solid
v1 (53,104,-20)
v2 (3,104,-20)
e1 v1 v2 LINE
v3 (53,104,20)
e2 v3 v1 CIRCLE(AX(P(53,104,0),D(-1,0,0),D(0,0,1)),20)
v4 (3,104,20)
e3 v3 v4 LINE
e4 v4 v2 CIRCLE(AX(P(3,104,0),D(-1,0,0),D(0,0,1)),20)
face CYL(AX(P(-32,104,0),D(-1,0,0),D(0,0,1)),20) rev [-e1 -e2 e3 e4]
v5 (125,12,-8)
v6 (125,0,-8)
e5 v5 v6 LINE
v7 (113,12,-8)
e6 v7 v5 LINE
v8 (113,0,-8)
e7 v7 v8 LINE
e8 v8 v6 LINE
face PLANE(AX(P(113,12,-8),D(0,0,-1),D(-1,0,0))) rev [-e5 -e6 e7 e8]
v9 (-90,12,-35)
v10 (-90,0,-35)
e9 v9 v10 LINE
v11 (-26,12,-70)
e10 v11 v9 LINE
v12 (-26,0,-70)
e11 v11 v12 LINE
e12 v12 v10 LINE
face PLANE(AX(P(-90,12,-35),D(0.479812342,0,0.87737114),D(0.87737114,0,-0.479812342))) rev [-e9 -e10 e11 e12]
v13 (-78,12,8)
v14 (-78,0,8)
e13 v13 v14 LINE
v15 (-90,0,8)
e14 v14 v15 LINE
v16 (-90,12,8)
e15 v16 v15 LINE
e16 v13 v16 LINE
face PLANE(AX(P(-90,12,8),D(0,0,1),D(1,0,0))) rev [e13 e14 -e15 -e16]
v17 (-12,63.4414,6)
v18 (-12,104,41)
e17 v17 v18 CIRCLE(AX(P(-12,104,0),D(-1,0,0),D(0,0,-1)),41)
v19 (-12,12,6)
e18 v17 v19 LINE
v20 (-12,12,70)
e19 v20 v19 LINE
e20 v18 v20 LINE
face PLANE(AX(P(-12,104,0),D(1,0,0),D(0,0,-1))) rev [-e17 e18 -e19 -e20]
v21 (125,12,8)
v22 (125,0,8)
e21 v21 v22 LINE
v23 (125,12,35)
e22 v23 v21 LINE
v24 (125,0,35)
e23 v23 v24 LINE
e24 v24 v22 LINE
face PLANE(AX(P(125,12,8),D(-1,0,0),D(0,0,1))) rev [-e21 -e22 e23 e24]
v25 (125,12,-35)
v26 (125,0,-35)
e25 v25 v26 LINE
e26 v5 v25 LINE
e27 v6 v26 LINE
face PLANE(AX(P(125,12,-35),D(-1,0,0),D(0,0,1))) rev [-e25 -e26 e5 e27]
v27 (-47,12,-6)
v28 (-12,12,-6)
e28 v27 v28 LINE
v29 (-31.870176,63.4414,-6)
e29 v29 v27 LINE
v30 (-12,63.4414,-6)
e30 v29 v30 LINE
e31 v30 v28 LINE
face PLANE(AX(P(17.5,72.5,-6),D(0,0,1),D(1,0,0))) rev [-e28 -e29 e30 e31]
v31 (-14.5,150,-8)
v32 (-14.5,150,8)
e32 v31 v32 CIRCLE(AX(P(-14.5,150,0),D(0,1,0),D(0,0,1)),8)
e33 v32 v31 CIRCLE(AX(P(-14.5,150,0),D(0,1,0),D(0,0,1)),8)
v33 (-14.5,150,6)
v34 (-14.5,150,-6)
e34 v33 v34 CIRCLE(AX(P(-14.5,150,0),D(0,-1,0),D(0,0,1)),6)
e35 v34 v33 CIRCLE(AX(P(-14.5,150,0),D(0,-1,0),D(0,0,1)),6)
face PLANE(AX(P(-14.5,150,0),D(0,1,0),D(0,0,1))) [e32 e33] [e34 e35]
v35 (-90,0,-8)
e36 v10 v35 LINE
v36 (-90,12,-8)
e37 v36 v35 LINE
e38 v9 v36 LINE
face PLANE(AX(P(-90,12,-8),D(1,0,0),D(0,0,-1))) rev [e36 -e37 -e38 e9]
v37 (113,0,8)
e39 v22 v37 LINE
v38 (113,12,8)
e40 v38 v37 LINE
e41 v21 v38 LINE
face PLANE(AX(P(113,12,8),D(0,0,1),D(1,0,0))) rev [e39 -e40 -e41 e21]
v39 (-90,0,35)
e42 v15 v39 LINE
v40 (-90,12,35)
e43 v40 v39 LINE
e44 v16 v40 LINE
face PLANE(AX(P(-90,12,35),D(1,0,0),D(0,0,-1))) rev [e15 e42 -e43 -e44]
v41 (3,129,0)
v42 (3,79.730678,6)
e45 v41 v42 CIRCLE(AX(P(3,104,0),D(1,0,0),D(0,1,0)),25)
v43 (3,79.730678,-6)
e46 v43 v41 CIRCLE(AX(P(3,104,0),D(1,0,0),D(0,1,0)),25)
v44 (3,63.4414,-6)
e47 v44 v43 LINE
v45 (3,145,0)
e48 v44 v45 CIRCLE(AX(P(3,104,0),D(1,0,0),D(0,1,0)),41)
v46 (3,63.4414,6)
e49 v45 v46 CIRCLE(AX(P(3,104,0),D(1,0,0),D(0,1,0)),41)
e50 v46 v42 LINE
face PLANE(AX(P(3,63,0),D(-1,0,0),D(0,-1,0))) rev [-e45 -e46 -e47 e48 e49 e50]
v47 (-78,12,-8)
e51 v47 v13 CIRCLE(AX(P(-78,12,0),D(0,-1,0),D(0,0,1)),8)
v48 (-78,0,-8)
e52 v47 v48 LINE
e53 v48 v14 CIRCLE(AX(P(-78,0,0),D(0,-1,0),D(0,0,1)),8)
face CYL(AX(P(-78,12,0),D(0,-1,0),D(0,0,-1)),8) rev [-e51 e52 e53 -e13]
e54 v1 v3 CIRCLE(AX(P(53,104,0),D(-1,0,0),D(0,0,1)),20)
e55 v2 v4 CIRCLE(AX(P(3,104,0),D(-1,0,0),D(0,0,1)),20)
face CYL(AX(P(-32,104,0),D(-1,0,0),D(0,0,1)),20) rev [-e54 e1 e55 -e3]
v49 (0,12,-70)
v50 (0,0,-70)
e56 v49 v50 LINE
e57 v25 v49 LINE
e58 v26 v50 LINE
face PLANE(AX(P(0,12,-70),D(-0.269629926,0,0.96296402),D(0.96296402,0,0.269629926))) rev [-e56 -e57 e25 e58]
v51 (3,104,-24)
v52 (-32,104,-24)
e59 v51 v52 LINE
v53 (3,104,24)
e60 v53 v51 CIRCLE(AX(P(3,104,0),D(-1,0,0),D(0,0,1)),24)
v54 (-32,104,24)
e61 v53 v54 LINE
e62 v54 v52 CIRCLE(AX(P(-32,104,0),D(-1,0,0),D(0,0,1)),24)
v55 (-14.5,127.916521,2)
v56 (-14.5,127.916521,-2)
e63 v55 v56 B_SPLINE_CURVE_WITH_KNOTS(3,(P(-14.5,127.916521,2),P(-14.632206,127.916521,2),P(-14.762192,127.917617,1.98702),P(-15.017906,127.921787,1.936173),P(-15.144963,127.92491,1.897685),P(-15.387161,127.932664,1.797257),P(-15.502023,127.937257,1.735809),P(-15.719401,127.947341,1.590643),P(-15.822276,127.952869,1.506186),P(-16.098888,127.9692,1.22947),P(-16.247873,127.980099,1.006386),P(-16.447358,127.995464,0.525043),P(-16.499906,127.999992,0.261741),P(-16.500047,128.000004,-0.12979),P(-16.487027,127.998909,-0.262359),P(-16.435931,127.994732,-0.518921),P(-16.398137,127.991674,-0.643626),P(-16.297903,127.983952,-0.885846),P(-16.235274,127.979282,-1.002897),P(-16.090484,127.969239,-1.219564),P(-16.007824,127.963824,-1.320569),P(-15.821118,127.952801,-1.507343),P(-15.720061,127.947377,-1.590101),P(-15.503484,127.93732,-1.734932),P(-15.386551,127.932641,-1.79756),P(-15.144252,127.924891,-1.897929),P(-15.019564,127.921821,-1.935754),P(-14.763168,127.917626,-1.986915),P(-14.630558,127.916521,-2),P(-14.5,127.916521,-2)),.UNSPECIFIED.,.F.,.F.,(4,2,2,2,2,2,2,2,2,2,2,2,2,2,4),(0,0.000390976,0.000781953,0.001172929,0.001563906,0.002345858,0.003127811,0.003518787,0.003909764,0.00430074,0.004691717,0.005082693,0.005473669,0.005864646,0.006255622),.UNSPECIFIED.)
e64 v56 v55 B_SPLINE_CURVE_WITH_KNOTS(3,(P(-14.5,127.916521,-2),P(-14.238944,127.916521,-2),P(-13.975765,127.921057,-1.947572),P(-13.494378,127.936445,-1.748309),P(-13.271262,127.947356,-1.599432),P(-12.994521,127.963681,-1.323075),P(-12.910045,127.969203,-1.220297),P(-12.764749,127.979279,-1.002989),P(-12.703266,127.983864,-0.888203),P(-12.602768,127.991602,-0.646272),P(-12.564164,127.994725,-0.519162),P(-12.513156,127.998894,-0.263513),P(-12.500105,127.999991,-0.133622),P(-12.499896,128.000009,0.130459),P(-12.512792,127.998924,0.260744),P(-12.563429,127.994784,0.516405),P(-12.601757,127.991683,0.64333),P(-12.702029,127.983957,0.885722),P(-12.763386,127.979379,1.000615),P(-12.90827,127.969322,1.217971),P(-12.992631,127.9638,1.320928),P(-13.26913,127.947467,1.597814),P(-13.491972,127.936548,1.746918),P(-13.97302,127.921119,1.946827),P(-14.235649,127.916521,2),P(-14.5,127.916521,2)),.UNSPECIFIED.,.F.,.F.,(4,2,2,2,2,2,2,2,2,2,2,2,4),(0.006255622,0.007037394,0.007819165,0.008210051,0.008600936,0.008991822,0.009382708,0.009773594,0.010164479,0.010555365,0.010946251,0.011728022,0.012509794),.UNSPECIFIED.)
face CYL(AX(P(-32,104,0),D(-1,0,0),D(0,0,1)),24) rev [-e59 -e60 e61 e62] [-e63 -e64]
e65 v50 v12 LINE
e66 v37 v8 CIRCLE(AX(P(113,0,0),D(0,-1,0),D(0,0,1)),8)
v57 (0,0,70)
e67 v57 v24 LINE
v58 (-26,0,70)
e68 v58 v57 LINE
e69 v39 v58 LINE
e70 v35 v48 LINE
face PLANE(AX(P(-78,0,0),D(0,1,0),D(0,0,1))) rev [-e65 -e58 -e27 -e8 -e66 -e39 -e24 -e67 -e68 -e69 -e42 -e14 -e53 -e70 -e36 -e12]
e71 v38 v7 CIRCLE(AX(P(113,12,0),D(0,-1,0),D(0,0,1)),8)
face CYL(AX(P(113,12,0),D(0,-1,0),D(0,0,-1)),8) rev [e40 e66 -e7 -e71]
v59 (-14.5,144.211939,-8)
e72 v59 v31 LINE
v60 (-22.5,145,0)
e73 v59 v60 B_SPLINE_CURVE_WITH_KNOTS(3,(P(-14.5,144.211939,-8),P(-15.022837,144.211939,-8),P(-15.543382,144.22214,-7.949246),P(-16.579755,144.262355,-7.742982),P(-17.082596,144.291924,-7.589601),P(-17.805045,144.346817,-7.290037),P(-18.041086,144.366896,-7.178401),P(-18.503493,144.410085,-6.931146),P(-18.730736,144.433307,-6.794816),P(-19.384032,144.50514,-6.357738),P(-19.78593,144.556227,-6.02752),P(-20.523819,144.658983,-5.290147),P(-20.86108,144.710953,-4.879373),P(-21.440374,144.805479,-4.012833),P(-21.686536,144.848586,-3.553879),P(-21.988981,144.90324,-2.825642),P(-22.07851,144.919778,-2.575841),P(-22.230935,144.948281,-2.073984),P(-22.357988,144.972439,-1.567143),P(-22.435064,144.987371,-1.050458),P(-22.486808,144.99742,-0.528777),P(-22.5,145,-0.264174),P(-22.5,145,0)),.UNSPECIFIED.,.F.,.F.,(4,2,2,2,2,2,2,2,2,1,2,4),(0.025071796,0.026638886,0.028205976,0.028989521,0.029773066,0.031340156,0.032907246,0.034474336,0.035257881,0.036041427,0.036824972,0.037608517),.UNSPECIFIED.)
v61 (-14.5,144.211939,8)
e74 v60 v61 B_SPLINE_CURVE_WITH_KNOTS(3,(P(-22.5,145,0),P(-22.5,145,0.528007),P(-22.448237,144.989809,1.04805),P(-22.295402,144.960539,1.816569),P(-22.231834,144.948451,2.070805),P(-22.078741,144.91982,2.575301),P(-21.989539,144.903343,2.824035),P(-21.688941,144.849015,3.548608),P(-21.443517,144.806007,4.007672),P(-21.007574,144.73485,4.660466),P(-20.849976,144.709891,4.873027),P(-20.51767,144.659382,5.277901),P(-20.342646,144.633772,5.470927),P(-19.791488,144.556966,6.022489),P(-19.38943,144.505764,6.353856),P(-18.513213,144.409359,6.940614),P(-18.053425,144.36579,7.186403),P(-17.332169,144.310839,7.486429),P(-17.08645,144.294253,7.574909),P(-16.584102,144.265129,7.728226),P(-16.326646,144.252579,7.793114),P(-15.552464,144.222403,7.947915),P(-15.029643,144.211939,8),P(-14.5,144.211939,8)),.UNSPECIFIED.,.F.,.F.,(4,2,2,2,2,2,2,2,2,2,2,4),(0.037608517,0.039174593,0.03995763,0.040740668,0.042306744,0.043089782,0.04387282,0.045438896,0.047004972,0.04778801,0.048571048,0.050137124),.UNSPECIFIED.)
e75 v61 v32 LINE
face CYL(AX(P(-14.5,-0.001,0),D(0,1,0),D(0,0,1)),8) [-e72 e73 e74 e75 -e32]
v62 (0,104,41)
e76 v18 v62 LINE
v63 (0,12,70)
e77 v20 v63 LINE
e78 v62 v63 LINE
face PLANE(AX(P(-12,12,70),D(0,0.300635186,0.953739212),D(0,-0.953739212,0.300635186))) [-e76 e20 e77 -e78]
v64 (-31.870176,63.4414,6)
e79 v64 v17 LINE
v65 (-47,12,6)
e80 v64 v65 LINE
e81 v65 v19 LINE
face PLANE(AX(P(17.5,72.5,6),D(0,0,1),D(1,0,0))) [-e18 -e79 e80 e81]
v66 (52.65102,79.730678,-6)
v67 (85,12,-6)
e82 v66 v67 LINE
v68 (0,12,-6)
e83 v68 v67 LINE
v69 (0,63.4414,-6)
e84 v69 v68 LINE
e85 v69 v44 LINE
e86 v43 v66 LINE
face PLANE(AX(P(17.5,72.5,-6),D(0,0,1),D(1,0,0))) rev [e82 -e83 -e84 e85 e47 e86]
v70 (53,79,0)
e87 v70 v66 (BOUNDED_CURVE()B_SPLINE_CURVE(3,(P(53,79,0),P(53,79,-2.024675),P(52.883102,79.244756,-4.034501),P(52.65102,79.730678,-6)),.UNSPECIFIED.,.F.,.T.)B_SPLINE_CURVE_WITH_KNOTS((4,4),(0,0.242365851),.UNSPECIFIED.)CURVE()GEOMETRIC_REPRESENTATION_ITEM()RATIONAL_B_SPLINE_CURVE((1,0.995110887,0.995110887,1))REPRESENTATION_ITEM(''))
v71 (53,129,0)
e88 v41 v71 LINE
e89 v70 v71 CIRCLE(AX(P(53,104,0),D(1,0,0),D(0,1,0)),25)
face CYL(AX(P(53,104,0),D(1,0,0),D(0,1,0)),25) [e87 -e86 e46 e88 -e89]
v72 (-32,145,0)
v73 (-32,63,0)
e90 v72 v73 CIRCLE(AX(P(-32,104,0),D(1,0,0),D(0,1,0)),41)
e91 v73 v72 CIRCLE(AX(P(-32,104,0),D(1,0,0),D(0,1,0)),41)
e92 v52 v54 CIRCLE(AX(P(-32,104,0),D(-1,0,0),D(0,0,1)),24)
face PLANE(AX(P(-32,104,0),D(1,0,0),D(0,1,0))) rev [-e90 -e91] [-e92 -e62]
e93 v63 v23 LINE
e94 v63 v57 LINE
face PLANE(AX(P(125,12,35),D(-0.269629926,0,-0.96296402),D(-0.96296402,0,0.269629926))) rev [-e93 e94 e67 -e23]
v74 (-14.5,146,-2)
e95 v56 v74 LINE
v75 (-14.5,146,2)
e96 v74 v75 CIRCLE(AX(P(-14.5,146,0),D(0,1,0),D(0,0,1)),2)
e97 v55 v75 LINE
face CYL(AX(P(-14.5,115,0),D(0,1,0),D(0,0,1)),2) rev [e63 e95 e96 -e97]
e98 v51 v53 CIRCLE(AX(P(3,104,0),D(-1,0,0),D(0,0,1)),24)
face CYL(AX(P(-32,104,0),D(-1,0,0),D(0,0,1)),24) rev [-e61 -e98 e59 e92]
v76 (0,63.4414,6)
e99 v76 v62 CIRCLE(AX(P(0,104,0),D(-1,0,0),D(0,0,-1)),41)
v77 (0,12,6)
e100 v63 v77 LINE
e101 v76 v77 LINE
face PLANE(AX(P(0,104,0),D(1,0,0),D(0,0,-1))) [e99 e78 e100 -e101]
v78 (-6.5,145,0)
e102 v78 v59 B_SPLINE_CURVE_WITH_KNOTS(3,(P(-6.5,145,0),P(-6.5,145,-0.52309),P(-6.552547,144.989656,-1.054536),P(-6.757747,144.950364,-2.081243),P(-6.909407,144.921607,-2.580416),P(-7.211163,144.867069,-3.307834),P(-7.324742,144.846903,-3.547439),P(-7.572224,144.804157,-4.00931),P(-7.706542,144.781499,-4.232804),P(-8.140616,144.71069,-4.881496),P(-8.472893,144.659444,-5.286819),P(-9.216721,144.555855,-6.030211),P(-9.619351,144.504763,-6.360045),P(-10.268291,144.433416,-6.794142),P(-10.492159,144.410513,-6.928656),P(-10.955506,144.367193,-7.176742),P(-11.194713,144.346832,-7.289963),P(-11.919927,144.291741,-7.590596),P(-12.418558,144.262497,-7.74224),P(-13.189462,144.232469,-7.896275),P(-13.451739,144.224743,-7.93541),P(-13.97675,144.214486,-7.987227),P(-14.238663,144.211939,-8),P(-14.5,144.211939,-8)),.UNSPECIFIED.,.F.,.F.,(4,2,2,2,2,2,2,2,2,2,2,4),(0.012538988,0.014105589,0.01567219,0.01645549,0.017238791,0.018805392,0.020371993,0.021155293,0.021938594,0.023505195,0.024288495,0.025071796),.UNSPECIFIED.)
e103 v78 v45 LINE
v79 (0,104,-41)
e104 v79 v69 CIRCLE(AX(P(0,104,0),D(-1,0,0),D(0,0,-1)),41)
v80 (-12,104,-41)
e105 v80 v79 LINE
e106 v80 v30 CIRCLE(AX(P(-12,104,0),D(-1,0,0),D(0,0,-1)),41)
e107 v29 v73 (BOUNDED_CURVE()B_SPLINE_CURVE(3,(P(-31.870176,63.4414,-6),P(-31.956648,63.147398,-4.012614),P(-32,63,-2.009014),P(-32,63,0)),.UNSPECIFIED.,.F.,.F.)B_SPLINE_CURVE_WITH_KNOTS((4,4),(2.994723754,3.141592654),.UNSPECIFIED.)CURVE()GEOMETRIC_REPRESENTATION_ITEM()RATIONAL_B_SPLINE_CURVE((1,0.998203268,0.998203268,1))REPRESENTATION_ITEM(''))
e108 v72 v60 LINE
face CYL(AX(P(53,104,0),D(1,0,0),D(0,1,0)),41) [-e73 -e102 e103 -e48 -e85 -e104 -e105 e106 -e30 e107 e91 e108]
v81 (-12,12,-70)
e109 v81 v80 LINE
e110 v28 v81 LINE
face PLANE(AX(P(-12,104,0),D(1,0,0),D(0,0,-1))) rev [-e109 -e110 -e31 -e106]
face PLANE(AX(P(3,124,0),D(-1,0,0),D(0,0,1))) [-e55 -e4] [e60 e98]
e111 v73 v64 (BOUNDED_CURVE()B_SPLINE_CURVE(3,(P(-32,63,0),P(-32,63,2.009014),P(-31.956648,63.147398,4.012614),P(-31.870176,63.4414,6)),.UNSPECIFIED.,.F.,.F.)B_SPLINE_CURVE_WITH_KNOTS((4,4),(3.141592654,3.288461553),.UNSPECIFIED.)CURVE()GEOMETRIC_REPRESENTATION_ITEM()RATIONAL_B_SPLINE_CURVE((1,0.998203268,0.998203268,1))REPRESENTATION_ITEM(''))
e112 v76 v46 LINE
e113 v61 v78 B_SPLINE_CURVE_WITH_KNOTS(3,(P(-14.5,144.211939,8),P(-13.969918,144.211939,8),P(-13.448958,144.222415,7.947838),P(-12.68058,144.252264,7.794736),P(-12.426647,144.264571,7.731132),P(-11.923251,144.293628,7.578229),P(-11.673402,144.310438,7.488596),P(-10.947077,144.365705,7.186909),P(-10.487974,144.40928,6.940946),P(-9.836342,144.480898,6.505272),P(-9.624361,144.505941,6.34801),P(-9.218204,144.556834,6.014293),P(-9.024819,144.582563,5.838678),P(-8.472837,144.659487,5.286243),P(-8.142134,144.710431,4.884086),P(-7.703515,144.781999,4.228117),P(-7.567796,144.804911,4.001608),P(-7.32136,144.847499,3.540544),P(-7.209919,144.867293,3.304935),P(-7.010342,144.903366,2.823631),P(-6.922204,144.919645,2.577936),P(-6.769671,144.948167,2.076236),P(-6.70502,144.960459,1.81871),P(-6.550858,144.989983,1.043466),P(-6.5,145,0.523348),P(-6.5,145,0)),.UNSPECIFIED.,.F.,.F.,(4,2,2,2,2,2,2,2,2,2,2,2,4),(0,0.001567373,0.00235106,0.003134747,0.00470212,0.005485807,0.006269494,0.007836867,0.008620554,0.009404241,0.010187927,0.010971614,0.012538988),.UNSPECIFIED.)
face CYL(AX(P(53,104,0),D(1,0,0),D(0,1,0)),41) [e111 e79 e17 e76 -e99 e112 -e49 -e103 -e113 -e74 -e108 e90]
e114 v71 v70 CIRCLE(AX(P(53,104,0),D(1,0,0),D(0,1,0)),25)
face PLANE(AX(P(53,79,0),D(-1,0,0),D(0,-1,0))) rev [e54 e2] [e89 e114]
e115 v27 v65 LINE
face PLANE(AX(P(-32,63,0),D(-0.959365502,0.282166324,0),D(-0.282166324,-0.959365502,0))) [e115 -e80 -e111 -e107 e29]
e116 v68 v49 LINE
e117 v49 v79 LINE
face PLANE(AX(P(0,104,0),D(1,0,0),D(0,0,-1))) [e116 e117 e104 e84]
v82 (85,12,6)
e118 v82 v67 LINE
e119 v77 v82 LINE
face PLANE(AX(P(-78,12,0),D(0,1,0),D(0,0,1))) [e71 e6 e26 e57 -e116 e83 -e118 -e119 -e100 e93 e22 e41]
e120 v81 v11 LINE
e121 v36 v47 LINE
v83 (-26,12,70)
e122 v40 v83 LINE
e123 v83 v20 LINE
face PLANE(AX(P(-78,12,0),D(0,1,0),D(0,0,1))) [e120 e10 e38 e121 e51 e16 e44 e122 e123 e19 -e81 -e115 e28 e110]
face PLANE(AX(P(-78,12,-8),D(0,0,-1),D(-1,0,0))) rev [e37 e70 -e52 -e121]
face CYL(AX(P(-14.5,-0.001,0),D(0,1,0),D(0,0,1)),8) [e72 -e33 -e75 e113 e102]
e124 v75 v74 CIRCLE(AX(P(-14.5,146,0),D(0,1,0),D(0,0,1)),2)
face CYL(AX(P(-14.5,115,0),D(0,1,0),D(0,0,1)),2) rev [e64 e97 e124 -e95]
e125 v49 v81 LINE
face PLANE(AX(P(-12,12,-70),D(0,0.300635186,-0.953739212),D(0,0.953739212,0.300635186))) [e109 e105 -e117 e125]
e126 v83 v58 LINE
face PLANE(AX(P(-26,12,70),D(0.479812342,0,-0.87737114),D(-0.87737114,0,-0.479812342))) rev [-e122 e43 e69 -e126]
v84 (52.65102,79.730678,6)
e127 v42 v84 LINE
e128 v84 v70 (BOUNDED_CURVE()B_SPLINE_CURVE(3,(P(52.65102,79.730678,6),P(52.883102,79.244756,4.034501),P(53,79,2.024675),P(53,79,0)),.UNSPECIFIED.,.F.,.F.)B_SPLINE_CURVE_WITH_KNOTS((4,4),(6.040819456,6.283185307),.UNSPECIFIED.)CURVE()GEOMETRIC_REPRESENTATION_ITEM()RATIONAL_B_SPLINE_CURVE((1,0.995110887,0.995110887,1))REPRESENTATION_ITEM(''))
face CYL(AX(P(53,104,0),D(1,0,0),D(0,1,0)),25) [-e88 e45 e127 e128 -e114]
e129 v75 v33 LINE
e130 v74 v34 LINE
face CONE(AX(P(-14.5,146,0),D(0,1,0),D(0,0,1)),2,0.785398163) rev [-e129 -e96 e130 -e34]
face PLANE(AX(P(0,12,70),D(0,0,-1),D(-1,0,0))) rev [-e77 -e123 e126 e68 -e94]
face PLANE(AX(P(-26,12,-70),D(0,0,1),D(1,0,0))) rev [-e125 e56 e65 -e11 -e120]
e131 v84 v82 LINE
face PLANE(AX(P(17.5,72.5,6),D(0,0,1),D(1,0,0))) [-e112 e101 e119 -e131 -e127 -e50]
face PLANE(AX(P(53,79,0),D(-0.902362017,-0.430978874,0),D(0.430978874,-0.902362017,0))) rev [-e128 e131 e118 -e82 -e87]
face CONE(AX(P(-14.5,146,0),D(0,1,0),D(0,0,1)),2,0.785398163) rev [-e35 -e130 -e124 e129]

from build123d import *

# Parameters (mm, degrees)
BASE_PLATE_DEPTH              = 12
SUPPORT_WEB_DEPTH             = 12
WEB_GUSSET_RIB_REACH          = 205.838
WEB_GUSSET_RIB_SKETCH_WALL_W  = 462.836477652
WEB_GUSSET_RIB_SKETCH_WALL_H  = 12
SIDE_GUSSET_RIB_REACH         = 205.838
SIDE_GUSSET_RIB_SKETCH_WALL_W = 483.925921336
SIDE_GUSSET_RIB_SKETCH_WALL_H = 12
GREASE_BOSS_16_REACH          = 209.425
GREASE_BOSS_16_END_RADIUS     = 41
GREASE_BOSS_SKETCH_R          = 8
LUBE_HOLE_SKETCH_R            = 2
LUBE_HOLE_DEPTH               = 35
GREASE_BOSS_CHAMFER_4X45_SIZE = 4


with BuildPart() as part:
    # Base Plate Sketch → Base Plate (new body)
    with BuildSketch(Plane(origin=(0, 0, 0), x_dir=(1, 0, 0), z_dir=(0, 1, 0))):
        with BuildLine():
            Line((-90, -35), (-90, -8))
            Line((-90, -8), (-78, -8))
            ThreePointArc((-78, -8), (-70, 0), (-78, 8))
            Line((-78, 8), (-90, 8))
            Line((-90, 8), (-90, 35))
            Line((-90, 35), (-26, 70))
            Line((-26, 70), (0, 70))
            Line((0, 70), (125, 35))
            Line((125, 35), (125, 8))
            Line((125, 8), (113, 8))
            ThreePointArc((113, 8), (105, 0), (113, -8))
            Line((113, -8), (125, -8))
            Line((125, -8), (125, -35))
            Line((125, -35), (0, -70))
            Line((0, -70), (-26, -70))
            Line((-26, -70), (-90, -35))
        make_face()
    extrude(amount=BASE_PLATE_DEPTH)



with BuildPart() as body_2:
    # Bearing Boss Profile → Bearing Boss (revolve)
    with BuildSketch(Plane.XY, mode=Mode.PRIVATE) as bearing_boss_sk:
        Polygon((53, 104), (-32, 104), (-32, 63), (3, 63), (3, 79), (53, 79), align=None)
    revolve(bearing_boss_sk.sketch.rotate(Axis((53, 104, 0), (-1, 0, 0)), 180), axis=Axis((53, 104, 0), (-1, 0, 0)))

    # Stepped Bore Profile → Stepped Bore (revolve, cut)
    with BuildSketch(Plane.XY, mode=Mode.PRIVATE) as stepped_bore_sk:
        Polygon((-32, 128), (3, 128), (3, 124), (53, 124), (53, 104), (-32, 104), align=None)
    revolve(stepped_bore_sk.sketch.rotate(Axis((-32, 104, 0), (1, 0, 0)), 90), axis=Axis((-32, 104, 0), (1, 0, 0)), mode=Mode.SUBTRACT)


with BuildPart() as part_1:
    add(part.part)

    add(body_2.part)  # Support Web merges body 2
    # Support Web Sketch → Support Web (add)
    with BuildSketch(Plane(origin=(0, 0, 0), x_dir=(0, 0, -1), z_dir=(1, 0, 0))):
        with BuildLine():
            Line((-70, 12), (-41, 104))
            ThreePointArc((-41, 104), (0, 63), (41, 104))
            Line((41, 104), (70, 12))
            Line((70, 12), (35, 12))
            Line((35, 12), (8, 12))
            Line((8, 12), (-8, 12))
            Line((-8, 12), (-35, 12))
            Line((-35, 12), (-70, 12))
        make_face()
    extrude(amount=-SUPPORT_WEB_DEPTH)

    # Web Gusset Rib Sketch wall → Web Gusset Rib (add, up to next)
    with BuildSketch(Plane(origin=(-39.5, 37.5, 0), x_dir=(-0.282166323992, -0.959365501571, 0), z_dir=(0.959365501571, -0.282166323992, 0)), mode=Mode.PRIVATE) as web_gusset_rib_sk1:
        Rectangle(WEB_GUSSET_RIB_SKETCH_WALL_W, WEB_GUSSET_RIB_SKETCH_WALL_H)
    web_gusset_rib_tool1 = extrude(web_gusset_rib_sk1.sketch, amount=WEB_GUSSET_RIB_REACH, mode=Mode.PRIVATE) - part_1.part
    add(web_gusset_rib_tool1.solids().sort_by_distance((-39.5, 37.5, 0))[0])

    # Side Gusset Rib Sketch wall → Side Gusset Rib (add, up to next)
    with BuildSketch(Plane(origin=(69, 45.5, 0), x_dir=(0.430978873925, -0.90236201728, 0), z_dir=(0.90236201728, 0.430978873925, 0)), mode=Mode.PRIVATE) as side_gusset_rib_sk1:
        Rectangle(SIDE_GUSSET_RIB_SKETCH_WALL_W, SIDE_GUSSET_RIB_SKETCH_WALL_H)
    side_gusset_rib_tool1 = extrude(side_gusset_rib_sk1.sketch, amount=-SIDE_GUSSET_RIB_REACH, mode=Mode.PRIVATE) - part_1.part
    add(side_gusset_rib_tool1.solids().sort_by_distance((69, 45.5, 0))[0])

    # Grease Boss Ø16: up to this cylinder (the profile starts outside it)
    grease_boss_16_end = Plane(origin=(-14.5, 104, 0), z_dir=(1, 0, 0)) * Cylinder(GREASE_BOSS_16_END_RADIUS, 501.85, mode=Mode.PRIVATE)
    # Grease Boss Sketch → Grease Boss Ø16 (add, up to the surface)
    with BuildSketch(Plane(origin=(0, 150, 0), x_dir=(1, 0, 0), z_dir=(0, 1, 0)), mode=Mode.PRIVATE) as grease_boss_16_sk1:
        with Locations(Location((-14.5, 0, 0), (0, 0, 270))):
            Circle(GREASE_BOSS_SKETCH_R)
    grease_boss_16_tool1 = extrude(grease_boss_16_sk1.sketch, amount=-GREASE_BOSS_16_REACH, mode=Mode.PRIVATE) - grease_boss_16_end
    add(grease_boss_16_tool1.solids().sort_by_distance((-14.5, 150, 0))[0])

    # Lube Hole Sketch → Lube Hole (cut)
    with BuildSketch(Plane(origin=(0, 150, 0), x_dir=(1, 0, 0), z_dir=(0, 1, 0))):
        with Locations(Location((-14.5, 0, 0), (0, 0, 270))):
            Circle(LUBE_HOLE_SKETCH_R)
    extrude(amount=-LUBE_HOLE_DEPTH, mode=Mode.SUBTRACT)

    # Grease Boss Chamfer 4x45°
    grease_boss_chamfer_4x45_edges = [part_1.edges().sort_by_distance(p)[0] for p in [
        (-14.5, 150, -2),
    ]]
    chamfer(grease_boss_chamfer_4x45_edges, length=GREASE_BOSS_CHAMFER_4X45_SIZE)


solid = part_1.part
